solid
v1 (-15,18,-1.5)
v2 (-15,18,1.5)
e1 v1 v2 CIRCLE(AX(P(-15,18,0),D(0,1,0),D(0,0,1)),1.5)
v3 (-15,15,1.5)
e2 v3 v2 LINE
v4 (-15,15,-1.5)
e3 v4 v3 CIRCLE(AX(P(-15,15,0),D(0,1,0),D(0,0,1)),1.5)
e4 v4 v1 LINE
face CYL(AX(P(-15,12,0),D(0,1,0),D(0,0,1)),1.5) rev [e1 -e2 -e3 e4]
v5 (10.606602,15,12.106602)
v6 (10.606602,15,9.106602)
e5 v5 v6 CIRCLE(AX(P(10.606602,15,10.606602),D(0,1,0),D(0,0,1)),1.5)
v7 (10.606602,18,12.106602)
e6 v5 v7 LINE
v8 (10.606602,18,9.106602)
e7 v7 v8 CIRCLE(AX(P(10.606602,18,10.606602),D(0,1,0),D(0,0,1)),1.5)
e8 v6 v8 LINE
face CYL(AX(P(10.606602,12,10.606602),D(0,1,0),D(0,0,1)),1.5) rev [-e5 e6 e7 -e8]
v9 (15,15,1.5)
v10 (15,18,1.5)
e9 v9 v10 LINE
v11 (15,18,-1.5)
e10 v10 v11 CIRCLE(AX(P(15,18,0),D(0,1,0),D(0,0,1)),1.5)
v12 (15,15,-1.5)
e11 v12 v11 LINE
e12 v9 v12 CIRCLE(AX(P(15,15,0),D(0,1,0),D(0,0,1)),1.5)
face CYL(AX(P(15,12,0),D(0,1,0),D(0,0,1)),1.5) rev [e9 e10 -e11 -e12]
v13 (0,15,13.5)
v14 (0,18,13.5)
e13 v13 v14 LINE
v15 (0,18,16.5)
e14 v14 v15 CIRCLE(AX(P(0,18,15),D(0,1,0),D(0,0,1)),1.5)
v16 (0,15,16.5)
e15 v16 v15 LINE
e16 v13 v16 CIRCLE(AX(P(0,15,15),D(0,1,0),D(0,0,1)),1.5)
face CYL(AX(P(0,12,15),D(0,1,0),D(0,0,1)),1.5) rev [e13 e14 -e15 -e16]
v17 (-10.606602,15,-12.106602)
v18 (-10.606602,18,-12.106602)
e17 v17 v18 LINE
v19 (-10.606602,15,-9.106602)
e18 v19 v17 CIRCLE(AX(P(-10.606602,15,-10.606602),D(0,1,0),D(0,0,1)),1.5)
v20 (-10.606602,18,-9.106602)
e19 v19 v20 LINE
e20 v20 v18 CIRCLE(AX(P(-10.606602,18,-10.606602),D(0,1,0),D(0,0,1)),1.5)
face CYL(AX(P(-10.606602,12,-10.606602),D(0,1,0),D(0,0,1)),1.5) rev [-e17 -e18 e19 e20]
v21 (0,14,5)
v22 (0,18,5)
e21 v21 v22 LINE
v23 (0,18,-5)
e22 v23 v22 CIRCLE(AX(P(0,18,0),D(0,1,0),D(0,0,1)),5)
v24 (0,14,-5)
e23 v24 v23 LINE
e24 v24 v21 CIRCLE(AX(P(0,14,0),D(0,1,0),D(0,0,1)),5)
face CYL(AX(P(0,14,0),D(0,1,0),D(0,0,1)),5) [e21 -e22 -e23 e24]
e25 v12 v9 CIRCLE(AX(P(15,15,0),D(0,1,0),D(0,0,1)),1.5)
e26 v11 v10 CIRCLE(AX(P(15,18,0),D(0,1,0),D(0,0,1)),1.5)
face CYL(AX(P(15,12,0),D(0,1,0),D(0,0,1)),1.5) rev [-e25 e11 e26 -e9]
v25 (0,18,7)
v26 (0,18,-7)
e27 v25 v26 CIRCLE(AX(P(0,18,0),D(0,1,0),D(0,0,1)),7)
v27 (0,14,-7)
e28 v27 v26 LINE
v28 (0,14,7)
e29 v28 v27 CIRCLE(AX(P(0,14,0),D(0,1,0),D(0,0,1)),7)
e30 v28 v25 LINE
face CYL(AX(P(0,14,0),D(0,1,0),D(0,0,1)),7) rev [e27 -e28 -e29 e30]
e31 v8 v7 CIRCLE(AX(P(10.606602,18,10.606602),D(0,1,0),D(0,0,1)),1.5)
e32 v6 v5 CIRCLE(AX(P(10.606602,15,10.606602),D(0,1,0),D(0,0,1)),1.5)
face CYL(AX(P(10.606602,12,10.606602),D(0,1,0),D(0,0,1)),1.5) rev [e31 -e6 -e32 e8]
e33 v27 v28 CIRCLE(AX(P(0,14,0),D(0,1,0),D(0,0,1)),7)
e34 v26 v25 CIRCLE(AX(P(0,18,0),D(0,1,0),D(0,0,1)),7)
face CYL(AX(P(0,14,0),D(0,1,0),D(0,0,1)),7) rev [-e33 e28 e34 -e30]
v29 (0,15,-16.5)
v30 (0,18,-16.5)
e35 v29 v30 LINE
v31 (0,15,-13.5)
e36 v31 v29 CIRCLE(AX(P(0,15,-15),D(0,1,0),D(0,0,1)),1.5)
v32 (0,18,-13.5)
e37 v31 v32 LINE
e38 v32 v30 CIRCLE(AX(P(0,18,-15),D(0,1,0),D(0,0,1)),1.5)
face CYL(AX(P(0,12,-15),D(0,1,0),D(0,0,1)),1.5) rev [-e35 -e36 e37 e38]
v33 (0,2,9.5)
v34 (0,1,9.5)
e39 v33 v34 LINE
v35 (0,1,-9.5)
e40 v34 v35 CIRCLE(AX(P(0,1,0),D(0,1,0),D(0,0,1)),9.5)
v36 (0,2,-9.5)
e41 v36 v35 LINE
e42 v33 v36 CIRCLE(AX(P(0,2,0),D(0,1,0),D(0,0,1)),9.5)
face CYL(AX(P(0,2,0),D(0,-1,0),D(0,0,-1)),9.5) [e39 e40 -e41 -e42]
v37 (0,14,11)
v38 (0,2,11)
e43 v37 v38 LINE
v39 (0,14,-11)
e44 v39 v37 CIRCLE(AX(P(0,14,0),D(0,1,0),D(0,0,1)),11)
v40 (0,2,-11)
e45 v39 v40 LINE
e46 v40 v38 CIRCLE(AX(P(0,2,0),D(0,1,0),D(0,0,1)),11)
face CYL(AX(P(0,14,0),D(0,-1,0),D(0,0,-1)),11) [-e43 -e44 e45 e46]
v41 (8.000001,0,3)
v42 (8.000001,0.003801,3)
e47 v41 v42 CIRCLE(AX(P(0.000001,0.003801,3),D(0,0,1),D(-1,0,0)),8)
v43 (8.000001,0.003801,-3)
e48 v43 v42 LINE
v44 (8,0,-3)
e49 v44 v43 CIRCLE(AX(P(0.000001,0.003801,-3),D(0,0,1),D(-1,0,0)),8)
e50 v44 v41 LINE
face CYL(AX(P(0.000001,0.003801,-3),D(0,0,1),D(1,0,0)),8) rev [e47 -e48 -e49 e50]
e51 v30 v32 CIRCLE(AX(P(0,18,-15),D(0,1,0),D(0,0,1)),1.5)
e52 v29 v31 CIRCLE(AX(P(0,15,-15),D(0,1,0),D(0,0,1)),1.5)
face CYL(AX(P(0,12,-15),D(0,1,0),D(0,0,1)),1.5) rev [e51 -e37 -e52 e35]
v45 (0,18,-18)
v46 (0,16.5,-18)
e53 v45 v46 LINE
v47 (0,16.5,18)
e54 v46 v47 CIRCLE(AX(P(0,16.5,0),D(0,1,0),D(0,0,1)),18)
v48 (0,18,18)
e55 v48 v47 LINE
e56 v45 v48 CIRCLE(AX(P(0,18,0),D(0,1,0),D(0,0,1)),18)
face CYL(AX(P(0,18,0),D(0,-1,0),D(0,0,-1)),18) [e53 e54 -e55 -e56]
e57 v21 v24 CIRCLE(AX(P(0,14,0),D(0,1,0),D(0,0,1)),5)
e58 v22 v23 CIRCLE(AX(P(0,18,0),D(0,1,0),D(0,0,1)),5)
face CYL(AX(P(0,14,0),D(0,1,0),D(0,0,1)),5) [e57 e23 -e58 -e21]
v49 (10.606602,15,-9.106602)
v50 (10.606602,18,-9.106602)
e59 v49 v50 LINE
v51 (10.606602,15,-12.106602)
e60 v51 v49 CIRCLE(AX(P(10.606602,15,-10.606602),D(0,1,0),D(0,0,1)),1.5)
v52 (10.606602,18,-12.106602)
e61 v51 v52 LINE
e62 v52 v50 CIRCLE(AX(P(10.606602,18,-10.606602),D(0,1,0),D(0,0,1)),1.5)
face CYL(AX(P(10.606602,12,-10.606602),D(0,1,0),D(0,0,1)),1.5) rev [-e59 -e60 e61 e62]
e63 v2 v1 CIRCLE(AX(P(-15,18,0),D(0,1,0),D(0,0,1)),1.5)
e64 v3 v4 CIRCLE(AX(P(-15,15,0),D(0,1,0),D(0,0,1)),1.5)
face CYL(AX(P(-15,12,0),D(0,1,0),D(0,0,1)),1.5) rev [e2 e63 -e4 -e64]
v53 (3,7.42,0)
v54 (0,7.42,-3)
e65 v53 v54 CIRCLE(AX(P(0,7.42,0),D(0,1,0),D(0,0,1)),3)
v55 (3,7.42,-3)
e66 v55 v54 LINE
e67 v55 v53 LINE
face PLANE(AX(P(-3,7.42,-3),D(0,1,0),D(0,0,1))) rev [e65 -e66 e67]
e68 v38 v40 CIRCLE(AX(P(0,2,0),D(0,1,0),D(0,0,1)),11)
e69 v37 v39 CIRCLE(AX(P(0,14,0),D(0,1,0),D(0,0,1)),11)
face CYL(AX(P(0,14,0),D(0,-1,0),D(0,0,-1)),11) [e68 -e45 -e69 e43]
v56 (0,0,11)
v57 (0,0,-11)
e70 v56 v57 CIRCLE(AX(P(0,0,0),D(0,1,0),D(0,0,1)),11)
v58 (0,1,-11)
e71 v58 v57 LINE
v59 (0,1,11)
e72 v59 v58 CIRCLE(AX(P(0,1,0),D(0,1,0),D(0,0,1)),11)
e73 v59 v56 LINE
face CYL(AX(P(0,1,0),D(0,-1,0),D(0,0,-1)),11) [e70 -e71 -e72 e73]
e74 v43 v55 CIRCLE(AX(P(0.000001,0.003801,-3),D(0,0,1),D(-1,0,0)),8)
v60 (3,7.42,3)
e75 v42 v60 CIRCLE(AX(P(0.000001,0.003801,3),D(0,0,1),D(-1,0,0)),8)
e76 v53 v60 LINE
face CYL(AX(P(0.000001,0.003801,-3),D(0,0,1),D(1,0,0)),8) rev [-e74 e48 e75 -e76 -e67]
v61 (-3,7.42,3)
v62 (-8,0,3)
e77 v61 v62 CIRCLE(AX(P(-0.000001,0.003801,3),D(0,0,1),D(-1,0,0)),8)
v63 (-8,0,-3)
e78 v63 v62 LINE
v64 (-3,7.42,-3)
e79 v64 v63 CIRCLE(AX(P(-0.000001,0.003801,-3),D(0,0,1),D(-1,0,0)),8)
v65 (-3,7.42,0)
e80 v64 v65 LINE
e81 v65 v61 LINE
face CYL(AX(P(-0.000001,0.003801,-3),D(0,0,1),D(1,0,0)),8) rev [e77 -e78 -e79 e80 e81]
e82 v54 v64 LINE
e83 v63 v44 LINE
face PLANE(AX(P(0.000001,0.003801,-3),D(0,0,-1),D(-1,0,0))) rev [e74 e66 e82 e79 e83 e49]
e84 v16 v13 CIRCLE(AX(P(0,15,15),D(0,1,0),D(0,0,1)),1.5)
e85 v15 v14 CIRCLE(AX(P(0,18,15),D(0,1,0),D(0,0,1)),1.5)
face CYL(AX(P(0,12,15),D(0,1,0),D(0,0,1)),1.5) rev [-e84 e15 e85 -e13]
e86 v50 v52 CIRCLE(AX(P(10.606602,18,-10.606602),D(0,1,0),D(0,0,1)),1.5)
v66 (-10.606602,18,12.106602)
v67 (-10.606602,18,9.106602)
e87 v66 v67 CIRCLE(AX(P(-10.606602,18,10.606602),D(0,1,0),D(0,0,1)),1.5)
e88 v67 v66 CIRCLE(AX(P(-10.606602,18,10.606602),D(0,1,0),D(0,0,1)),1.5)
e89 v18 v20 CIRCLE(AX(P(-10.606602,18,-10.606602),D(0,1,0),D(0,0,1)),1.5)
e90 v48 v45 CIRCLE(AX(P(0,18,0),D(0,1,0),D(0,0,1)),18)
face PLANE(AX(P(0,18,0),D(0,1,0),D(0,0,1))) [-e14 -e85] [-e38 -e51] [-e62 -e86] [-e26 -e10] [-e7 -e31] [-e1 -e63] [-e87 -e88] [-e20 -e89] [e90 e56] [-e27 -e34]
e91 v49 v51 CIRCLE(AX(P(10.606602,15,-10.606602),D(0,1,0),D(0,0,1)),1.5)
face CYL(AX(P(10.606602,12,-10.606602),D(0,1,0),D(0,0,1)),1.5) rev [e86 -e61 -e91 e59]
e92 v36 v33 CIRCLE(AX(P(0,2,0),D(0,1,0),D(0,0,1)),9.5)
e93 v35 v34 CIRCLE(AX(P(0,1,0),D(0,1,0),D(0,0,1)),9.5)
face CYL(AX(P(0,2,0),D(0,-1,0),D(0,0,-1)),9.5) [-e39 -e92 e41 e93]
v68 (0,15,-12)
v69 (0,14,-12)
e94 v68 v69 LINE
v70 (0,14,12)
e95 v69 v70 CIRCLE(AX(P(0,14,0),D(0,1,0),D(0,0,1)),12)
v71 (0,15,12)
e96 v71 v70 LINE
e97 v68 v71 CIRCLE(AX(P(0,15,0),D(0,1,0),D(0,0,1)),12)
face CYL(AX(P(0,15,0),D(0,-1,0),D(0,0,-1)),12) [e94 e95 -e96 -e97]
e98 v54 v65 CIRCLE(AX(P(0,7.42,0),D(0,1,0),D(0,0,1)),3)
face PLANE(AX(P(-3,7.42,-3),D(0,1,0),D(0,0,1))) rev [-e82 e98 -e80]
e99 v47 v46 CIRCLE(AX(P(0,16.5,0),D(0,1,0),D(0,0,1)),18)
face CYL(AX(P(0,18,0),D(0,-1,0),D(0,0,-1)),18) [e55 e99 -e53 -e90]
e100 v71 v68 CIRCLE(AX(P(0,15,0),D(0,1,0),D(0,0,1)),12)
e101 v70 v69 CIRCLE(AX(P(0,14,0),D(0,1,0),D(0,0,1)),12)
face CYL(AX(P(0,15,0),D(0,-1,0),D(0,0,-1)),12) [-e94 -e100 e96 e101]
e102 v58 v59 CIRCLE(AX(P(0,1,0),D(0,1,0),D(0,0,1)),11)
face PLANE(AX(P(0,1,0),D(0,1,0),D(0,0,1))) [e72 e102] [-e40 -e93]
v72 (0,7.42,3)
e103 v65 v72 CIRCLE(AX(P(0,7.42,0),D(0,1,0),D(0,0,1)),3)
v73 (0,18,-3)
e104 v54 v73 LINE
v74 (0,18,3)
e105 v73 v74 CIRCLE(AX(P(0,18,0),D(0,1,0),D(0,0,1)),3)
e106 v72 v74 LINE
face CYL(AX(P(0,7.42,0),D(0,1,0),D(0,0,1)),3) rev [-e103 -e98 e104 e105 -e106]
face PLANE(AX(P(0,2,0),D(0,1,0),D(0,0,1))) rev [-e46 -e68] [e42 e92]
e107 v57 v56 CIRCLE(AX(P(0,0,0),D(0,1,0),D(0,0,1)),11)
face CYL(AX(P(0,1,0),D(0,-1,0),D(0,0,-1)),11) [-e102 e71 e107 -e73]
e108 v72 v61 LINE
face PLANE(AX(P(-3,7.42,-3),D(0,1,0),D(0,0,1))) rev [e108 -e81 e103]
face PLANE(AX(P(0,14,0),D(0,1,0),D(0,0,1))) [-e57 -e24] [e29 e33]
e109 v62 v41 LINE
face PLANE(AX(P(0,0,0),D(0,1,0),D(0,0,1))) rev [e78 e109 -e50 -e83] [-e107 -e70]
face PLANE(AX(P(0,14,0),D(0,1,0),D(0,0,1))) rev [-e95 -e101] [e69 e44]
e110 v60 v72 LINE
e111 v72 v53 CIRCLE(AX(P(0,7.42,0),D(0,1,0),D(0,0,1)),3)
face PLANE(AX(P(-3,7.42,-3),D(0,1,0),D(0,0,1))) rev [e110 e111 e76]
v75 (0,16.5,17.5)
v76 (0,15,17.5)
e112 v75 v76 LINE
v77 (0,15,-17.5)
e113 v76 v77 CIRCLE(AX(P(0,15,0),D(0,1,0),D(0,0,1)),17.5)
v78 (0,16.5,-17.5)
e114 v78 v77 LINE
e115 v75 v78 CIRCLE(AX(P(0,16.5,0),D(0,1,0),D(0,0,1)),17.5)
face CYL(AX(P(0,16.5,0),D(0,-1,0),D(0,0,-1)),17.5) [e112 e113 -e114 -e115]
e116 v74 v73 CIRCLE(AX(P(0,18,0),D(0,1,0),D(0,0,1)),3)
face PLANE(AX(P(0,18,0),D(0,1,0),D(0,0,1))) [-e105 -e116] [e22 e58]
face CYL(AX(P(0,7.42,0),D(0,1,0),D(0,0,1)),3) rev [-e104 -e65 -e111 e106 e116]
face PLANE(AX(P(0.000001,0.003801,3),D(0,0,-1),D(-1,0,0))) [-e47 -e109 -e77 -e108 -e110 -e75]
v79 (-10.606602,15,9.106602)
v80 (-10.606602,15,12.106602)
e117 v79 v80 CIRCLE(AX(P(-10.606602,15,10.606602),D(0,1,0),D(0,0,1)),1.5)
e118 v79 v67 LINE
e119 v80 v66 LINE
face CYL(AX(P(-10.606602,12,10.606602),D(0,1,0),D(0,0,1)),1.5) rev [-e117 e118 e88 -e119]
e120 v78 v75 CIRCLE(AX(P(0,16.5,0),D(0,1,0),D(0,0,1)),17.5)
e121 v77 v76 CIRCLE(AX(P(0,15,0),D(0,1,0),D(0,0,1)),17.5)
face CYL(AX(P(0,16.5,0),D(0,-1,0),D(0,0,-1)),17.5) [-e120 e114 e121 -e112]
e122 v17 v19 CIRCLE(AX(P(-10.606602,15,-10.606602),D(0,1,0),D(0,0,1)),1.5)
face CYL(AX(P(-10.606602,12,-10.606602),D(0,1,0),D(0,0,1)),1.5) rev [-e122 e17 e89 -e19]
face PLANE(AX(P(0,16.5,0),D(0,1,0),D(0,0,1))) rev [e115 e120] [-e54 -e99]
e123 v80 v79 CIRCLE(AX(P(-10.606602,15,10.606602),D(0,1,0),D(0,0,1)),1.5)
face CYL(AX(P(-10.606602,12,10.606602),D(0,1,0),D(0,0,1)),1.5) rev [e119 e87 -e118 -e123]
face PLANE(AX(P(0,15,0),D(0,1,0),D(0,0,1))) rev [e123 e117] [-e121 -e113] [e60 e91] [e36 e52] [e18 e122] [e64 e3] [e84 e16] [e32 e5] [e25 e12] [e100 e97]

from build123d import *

# Parameters (mm, degrees)
BASE_LIP_SKETCH_22_R       = 11
BASE_LIP_22_DEPTH          = 1
GROOVE_SKETCH_19_R         = 9.5
GROOVE_NECK_19_DEPTH       = 1
SHANK_SKETCH_22_R          = 11
SHANK_22_DEPTH             = 12
COLLAR_SKETCH_24_R         = 12
COLLAR_24_DEPTH            = 1
FLANGE_LOWER_SKETCH_35_R   = 17.5
FLANGE_LOWER_STEP_35_DEPTH = 1.5
FLANGE_SKETCH_36_R         = 18
FLANGE_36_DEPTH            = 1.5
SIDE_WINDOW_CUT_DEPTH      = 3
BOLT_HOLES_SKETCH_8X_3_R   = 1.5
BOLT_HOLES_8X_3_DEPTH      = 6
RECESS_SKETCH_14_R         = 7
RECESS_14_DEPTH            = 4
INNER_SPIGOT_SKETCH_10_R   = 5
INNER_SPIGOT_10_DEPTH      = 4
BORE_SKETCH_6_R            = 3
THROUGH_BORE_6_DEPTH       = 10.58


with BuildPart() as part:
    # Base Lip Sketch Ø22 → Base Lip Ø22 (new body)
    with BuildSketch(Plane(origin=(0, 0, 0), x_dir=(1, 0, 0), z_dir=(0, 1, 0))):
        with Locations(Location((0, 0, 0), (0, 0, 270))):
            Circle(BASE_LIP_SKETCH_22_R)
    extrude(amount=BASE_LIP_22_DEPTH)

    # Groove Sketch Ø19 → Groove Neck Ø19 (add)
    with BuildSketch(Plane(origin=(0, 1, 0), x_dir=(1, 0, 0), z_dir=(0, 1, 0))):
        with Locations(Location((0, 0, 0), (0, 0, 270))):
            Circle(GROOVE_SKETCH_19_R)
    extrude(amount=GROOVE_NECK_19_DEPTH)

    # Shank Sketch Ø22 → Shank Ø22 (add)
    with BuildSketch(Plane(origin=(0, 2, 0), x_dir=(1, 0, 0), z_dir=(0, 1, 0))):
        with Locations(Location((0, 0, 0), (0, 0, 270))):
            Circle(SHANK_SKETCH_22_R)
    extrude(amount=SHANK_22_DEPTH)

    # Collar Sketch Ø24 → Collar Ø24 (add)
    with BuildSketch(Plane(origin=(0, 14, 0), x_dir=(1, 0, 0), z_dir=(0, 1, 0))):
        with Locations(Location((0, 0, 0), (0, 0, 270))):
            Circle(COLLAR_SKETCH_24_R)
    extrude(amount=COLLAR_24_DEPTH)

    # Flange Lower Sketch Ø35 → Flange Lower Step Ø35 (add)
    with BuildSketch(Plane(origin=(0, 15, 0), x_dir=(1, 0, 0), z_dir=(0, 1, 0))):
        with Locations(Location((0, 0, 0), (0, 0, 270))):
            Circle(FLANGE_LOWER_SKETCH_35_R)
    extrude(amount=FLANGE_LOWER_STEP_35_DEPTH)

    # Flange Sketch Ø36 → Flange Ø36 (add)
    with BuildSketch(Plane(origin=(0, 16.5, 0), x_dir=(1, 0, 0), z_dir=(0, 1, 0))):
        with Locations(Location((0, 0, 0), (0, 0, 270))):
            Circle(FLANGE_SKETCH_36_R)
    extrude(amount=FLANGE_36_DEPTH)

    # Side Window Sketch → Side Window Cut (cut, symmetric)
    with BuildSketch(Plane.XY):
        with BuildLine():
            Line((-8, 0), (8, 0))
            ThreePointArc((8, 0), (6.634312477, 4.474361508), (3, 7.42))
            Line((3, 7.42), (-3, 7.42))
            ThreePointArc((-3, 7.42), (-6.634312477, 4.474361508), (-8, 0))
        make_face()
    extrude(amount=SIDE_WINDOW_CUT_DEPTH, both=True, mode=Mode.SUBTRACT)

    # Bolt Holes Sketch 8xØ3 → Bolt Holes 8xØ3 (cut)
    with BuildSketch(Plane(origin=(0, 18, 0), x_dir=(1, 0, 0), z_dir=(0, 1, 0))):
        with Locations(Location((0, 15, 0), (0, 0, 270))):
            Circle(BOLT_HOLES_SKETCH_8X_3_R)
        with Locations(Location((10.606601718, 10.606601718, 0), (0, 0, 270))):
            Circle(BOLT_HOLES_SKETCH_8X_3_R)
        with Locations(Location((15, 0, 0), (0, 0, 270))):
            Circle(BOLT_HOLES_SKETCH_8X_3_R)
        with Locations(Location((10.606601718, -10.606601718, 0), (0, 0, 270))):
            Circle(BOLT_HOLES_SKETCH_8X_3_R)
        with Locations(Location((0, -15, 0), (0, 0, 270))):
            Circle(BOLT_HOLES_SKETCH_8X_3_R)
        with Locations(Location((-10.606601718, -10.606601718, 0), (0, 0, 270))):
            Circle(BOLT_HOLES_SKETCH_8X_3_R)
        with Locations(Location((-15, 0, 0), (0, 0, 270))):
            Circle(BOLT_HOLES_SKETCH_8X_3_R)
        with Locations(Location((-10.606601718, 10.606601718, 0), (0, 0, 270))):
            Circle(BOLT_HOLES_SKETCH_8X_3_R)
    extrude(amount=-BOLT_HOLES_8X_3_DEPTH, mode=Mode.SUBTRACT)

    # Recess Sketch Ø14 → Recess Ø14 (cut)
    with BuildSketch(Plane(origin=(0, 18, 0), x_dir=(1, 0, 0), z_dir=(0, 1, 0))):
        with Locations(Location((0, 0, 0), (0, 0, 270))):
            Circle(RECESS_SKETCH_14_R)
    extrude(amount=-RECESS_14_DEPTH, mode=Mode.SUBTRACT)

    # Inner Spigot Sketch Ø10 → Inner Spigot Ø10 (add)
    with BuildSketch(Plane(origin=(0, 18, 0), x_dir=(1, 0, 0), z_dir=(0, 1, 0))):
        with Locations(Location((0, 0, 0), (0, 0, 270))):
            Circle(INNER_SPIGOT_SKETCH_10_R)
    extrude(amount=-INNER_SPIGOT_10_DEPTH)

    # Bore Sketch Ø6 → Through Bore Ø6 (cut)
    with BuildSketch(Plane(origin=(0, 18, 0), x_dir=(1, 0, 0), z_dir=(0, 1, 0))):
        with Locations(Location((0, 0, 0), (0, 0, 270))):
            Circle(BORE_SKETCH_6_R)
    extrude(amount=-THROUGH_BORE_6_DEPTH, mode=Mode.SUBTRACT)


solid = part.part
